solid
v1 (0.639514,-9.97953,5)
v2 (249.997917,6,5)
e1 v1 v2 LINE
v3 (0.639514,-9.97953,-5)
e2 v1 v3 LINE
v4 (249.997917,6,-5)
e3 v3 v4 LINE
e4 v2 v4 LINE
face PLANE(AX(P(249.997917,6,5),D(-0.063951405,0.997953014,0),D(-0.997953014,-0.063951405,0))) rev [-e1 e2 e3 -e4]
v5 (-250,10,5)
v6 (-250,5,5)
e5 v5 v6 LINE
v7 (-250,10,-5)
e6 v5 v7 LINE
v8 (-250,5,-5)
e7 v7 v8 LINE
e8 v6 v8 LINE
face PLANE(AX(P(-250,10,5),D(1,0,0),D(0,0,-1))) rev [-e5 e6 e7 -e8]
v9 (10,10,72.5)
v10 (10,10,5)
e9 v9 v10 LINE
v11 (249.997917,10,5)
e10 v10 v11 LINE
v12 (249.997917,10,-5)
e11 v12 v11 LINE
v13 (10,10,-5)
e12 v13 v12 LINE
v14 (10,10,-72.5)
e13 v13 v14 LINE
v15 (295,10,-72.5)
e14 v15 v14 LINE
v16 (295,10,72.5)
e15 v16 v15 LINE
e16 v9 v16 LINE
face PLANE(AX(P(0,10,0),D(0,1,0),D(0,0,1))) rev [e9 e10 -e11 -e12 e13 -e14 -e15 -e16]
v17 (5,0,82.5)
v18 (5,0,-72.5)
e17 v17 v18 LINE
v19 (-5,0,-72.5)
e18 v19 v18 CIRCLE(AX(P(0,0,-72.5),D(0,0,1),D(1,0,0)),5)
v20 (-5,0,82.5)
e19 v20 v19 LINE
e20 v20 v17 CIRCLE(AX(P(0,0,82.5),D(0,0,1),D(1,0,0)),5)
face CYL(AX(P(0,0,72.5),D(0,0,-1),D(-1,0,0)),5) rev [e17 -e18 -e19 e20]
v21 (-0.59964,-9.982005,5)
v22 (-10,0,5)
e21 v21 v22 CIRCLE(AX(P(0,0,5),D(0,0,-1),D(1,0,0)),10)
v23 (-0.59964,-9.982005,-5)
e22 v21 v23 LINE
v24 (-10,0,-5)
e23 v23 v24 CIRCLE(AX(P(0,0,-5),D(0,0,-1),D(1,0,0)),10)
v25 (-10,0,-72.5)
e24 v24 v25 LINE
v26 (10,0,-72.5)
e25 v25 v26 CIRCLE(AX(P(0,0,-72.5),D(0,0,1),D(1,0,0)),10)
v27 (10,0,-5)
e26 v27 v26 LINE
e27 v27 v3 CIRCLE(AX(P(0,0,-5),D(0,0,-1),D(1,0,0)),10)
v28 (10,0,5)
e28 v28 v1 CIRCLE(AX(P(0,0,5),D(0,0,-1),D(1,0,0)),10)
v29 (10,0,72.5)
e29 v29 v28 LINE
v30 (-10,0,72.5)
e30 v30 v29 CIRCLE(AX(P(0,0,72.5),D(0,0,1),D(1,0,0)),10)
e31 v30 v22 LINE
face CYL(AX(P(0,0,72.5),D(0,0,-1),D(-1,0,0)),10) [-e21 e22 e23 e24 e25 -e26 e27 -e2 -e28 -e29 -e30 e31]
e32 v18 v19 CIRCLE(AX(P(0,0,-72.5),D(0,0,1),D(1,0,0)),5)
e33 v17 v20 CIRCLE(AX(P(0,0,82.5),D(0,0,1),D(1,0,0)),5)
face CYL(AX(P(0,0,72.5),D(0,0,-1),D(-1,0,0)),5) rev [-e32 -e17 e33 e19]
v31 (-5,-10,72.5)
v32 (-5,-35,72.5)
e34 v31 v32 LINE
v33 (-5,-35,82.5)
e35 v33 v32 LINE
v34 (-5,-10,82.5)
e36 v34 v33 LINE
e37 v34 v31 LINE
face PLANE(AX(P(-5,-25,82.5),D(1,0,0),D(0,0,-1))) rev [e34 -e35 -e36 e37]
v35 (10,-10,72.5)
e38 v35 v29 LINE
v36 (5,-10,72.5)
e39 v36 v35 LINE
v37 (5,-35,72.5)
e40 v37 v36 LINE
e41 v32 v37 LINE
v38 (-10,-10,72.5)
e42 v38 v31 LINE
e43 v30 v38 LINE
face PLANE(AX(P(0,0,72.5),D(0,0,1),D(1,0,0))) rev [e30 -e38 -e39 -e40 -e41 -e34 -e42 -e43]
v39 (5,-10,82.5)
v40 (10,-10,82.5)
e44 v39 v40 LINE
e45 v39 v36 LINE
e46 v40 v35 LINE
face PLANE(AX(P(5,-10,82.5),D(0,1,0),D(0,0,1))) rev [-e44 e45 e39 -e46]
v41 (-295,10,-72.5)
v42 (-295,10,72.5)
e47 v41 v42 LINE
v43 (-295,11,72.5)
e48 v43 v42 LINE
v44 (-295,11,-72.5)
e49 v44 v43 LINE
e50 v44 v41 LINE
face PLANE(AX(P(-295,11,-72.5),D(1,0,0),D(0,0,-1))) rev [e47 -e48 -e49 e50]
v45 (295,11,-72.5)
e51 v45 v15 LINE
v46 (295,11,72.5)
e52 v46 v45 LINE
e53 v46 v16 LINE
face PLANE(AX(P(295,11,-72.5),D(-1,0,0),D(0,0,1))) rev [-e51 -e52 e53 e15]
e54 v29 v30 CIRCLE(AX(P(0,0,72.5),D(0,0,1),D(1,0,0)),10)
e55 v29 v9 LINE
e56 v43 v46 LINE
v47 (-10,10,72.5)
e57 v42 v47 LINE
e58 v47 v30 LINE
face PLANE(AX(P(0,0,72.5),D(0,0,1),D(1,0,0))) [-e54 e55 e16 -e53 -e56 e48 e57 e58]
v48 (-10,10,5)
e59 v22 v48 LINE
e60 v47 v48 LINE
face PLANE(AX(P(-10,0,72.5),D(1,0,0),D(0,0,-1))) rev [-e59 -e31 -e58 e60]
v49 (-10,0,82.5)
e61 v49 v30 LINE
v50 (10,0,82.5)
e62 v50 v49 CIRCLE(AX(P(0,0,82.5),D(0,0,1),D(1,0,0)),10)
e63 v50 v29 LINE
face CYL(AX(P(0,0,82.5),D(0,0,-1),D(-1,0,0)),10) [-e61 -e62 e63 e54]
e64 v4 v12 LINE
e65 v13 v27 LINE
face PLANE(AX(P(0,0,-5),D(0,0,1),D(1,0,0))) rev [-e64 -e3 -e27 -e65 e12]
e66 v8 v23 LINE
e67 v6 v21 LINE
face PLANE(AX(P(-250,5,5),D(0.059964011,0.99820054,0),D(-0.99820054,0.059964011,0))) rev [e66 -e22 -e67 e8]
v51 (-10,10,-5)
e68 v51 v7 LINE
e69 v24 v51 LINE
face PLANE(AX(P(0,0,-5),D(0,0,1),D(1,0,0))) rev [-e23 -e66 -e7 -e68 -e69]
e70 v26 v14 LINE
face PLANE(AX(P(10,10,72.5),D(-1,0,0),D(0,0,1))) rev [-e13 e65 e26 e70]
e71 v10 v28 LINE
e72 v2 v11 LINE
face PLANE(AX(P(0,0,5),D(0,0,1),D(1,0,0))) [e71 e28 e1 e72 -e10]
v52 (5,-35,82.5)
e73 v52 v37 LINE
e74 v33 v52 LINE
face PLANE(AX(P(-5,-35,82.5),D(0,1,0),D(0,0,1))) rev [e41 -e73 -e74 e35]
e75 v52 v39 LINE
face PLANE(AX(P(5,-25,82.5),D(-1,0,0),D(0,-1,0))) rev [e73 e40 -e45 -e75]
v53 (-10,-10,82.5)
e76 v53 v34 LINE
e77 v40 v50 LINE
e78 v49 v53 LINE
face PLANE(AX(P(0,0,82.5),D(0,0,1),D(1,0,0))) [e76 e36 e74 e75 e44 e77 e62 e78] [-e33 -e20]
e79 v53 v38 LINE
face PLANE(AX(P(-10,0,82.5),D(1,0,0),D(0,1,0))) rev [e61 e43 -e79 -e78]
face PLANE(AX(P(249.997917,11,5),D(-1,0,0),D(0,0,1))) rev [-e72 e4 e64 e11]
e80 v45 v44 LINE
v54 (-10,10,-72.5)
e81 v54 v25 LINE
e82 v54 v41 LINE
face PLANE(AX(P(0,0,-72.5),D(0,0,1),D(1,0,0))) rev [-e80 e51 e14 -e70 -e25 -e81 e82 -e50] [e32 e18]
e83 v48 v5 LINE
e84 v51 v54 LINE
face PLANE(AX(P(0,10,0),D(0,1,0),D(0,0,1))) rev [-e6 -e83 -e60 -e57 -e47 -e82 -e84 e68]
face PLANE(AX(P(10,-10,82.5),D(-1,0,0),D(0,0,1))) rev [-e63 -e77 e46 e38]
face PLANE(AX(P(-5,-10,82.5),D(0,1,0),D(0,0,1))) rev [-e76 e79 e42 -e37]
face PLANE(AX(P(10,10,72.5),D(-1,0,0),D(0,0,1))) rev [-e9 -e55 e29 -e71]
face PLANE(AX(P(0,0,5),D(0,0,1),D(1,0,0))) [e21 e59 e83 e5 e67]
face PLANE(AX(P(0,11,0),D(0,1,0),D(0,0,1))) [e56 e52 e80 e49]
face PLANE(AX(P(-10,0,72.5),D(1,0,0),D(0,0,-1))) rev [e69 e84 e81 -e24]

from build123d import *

# Parameters (mm, degrees)
SKETCH_1_R      = 5
EXTRUDE_1_DEPTH = 72.5
SKETCH_2_W      = 590
SKETCH_2_H      = 145
EXTRUDE_2_DEPTH = 1
EXTRUDE_3_DEPTH = 5
SKETCH_5_R      = 5
EXTRUDE_4_DEPTH = 10


with BuildPart() as part:
    # 草图1 → 凸台-拉伸1 (new, symmetric)
    with BuildSketch(Plane.XY):
        with BuildLine():
            Line((-10, 0), (-10, 10))
            Line((-10, 10), (10, 10))
            Line((10, 10), (10, 0))
            ThreePointArc((10, 0), (0, -10), (-10, 0))
        make_face()
        Circle(SKETCH_1_R, mode=Mode.SUBTRACT)
    extrude(amount=EXTRUDE_1_DEPTH, both=True)



with BuildPart() as body_2:
    # 草图2 → 凸台-拉伸2 (new body)
    with BuildSketch(Plane(origin=(0, 10, 0), x_dir=(1, 0, 0), z_dir=(0, 1, 0))):
        Rectangle(SKETCH_2_W, SKETCH_2_H)
    extrude(amount=EXTRUDE_2_DEPTH)


with BuildPart() as part_1:
    add(part.part)

    add(body_2.part)  # 凸台-拉伸3 merges body 2
    # 草图4 → 凸台-拉伸3 (add, symmetric)
    with BuildSketch(Plane.XY):
        with BuildLine():
            Line((-10, 10), (-250, 10))
            Line((-250, 10), (-250, 5))
            Line((-250, 5), (-0.599640103, -9.982005397))
            ThreePointArc((-0.599640103, -9.982005397), (-7.279986299, -6.85578584), (-10, 0))
            Line((-10, 0), (-10, 10))
        make_face()
        with BuildLine():
            Line((10, 10), (249.997916658, 11))
            Line((249.997916658, 11), (249.997916658, 6))
            Line((249.997916658, 6), (0.639514993, -9.979530078))
            ThreePointArc((0.639514993, -9.979530078), (7.293666771, -6.84122979), (10, 0))
            Line((10, 0), (10, 10))
        make_face()
    extrude(amount=EXTRUDE_3_DEPTH, both=True)

    # 草图5 → 凸台-拉伸4 (add)
    with BuildSketch(Plane.XY.offset(72.5)):
        with BuildLine():
            Line((-10, 0), (-10, -10))
            Line((-10, -10), (-5, -10))
            Line((-5, -10), (-5, -25))
            Line((-5, -25), (-5, -35))
            Line((-5, -35), (5, -35))
            Line((5, -35), (5, -25))
            Line((5, -25), (5, -10))
            Line((5, -10), (10, -10))
            Line((10, -10), (10, 0))
            ThreePointArc((10, 0), (0, 10), (-10, 0))
        make_face()
        Circle(SKETCH_5_R, mode=Mode.SUBTRACT)
    extrude(amount=EXTRUDE_4_DEPTH)


solid = part_1.part
